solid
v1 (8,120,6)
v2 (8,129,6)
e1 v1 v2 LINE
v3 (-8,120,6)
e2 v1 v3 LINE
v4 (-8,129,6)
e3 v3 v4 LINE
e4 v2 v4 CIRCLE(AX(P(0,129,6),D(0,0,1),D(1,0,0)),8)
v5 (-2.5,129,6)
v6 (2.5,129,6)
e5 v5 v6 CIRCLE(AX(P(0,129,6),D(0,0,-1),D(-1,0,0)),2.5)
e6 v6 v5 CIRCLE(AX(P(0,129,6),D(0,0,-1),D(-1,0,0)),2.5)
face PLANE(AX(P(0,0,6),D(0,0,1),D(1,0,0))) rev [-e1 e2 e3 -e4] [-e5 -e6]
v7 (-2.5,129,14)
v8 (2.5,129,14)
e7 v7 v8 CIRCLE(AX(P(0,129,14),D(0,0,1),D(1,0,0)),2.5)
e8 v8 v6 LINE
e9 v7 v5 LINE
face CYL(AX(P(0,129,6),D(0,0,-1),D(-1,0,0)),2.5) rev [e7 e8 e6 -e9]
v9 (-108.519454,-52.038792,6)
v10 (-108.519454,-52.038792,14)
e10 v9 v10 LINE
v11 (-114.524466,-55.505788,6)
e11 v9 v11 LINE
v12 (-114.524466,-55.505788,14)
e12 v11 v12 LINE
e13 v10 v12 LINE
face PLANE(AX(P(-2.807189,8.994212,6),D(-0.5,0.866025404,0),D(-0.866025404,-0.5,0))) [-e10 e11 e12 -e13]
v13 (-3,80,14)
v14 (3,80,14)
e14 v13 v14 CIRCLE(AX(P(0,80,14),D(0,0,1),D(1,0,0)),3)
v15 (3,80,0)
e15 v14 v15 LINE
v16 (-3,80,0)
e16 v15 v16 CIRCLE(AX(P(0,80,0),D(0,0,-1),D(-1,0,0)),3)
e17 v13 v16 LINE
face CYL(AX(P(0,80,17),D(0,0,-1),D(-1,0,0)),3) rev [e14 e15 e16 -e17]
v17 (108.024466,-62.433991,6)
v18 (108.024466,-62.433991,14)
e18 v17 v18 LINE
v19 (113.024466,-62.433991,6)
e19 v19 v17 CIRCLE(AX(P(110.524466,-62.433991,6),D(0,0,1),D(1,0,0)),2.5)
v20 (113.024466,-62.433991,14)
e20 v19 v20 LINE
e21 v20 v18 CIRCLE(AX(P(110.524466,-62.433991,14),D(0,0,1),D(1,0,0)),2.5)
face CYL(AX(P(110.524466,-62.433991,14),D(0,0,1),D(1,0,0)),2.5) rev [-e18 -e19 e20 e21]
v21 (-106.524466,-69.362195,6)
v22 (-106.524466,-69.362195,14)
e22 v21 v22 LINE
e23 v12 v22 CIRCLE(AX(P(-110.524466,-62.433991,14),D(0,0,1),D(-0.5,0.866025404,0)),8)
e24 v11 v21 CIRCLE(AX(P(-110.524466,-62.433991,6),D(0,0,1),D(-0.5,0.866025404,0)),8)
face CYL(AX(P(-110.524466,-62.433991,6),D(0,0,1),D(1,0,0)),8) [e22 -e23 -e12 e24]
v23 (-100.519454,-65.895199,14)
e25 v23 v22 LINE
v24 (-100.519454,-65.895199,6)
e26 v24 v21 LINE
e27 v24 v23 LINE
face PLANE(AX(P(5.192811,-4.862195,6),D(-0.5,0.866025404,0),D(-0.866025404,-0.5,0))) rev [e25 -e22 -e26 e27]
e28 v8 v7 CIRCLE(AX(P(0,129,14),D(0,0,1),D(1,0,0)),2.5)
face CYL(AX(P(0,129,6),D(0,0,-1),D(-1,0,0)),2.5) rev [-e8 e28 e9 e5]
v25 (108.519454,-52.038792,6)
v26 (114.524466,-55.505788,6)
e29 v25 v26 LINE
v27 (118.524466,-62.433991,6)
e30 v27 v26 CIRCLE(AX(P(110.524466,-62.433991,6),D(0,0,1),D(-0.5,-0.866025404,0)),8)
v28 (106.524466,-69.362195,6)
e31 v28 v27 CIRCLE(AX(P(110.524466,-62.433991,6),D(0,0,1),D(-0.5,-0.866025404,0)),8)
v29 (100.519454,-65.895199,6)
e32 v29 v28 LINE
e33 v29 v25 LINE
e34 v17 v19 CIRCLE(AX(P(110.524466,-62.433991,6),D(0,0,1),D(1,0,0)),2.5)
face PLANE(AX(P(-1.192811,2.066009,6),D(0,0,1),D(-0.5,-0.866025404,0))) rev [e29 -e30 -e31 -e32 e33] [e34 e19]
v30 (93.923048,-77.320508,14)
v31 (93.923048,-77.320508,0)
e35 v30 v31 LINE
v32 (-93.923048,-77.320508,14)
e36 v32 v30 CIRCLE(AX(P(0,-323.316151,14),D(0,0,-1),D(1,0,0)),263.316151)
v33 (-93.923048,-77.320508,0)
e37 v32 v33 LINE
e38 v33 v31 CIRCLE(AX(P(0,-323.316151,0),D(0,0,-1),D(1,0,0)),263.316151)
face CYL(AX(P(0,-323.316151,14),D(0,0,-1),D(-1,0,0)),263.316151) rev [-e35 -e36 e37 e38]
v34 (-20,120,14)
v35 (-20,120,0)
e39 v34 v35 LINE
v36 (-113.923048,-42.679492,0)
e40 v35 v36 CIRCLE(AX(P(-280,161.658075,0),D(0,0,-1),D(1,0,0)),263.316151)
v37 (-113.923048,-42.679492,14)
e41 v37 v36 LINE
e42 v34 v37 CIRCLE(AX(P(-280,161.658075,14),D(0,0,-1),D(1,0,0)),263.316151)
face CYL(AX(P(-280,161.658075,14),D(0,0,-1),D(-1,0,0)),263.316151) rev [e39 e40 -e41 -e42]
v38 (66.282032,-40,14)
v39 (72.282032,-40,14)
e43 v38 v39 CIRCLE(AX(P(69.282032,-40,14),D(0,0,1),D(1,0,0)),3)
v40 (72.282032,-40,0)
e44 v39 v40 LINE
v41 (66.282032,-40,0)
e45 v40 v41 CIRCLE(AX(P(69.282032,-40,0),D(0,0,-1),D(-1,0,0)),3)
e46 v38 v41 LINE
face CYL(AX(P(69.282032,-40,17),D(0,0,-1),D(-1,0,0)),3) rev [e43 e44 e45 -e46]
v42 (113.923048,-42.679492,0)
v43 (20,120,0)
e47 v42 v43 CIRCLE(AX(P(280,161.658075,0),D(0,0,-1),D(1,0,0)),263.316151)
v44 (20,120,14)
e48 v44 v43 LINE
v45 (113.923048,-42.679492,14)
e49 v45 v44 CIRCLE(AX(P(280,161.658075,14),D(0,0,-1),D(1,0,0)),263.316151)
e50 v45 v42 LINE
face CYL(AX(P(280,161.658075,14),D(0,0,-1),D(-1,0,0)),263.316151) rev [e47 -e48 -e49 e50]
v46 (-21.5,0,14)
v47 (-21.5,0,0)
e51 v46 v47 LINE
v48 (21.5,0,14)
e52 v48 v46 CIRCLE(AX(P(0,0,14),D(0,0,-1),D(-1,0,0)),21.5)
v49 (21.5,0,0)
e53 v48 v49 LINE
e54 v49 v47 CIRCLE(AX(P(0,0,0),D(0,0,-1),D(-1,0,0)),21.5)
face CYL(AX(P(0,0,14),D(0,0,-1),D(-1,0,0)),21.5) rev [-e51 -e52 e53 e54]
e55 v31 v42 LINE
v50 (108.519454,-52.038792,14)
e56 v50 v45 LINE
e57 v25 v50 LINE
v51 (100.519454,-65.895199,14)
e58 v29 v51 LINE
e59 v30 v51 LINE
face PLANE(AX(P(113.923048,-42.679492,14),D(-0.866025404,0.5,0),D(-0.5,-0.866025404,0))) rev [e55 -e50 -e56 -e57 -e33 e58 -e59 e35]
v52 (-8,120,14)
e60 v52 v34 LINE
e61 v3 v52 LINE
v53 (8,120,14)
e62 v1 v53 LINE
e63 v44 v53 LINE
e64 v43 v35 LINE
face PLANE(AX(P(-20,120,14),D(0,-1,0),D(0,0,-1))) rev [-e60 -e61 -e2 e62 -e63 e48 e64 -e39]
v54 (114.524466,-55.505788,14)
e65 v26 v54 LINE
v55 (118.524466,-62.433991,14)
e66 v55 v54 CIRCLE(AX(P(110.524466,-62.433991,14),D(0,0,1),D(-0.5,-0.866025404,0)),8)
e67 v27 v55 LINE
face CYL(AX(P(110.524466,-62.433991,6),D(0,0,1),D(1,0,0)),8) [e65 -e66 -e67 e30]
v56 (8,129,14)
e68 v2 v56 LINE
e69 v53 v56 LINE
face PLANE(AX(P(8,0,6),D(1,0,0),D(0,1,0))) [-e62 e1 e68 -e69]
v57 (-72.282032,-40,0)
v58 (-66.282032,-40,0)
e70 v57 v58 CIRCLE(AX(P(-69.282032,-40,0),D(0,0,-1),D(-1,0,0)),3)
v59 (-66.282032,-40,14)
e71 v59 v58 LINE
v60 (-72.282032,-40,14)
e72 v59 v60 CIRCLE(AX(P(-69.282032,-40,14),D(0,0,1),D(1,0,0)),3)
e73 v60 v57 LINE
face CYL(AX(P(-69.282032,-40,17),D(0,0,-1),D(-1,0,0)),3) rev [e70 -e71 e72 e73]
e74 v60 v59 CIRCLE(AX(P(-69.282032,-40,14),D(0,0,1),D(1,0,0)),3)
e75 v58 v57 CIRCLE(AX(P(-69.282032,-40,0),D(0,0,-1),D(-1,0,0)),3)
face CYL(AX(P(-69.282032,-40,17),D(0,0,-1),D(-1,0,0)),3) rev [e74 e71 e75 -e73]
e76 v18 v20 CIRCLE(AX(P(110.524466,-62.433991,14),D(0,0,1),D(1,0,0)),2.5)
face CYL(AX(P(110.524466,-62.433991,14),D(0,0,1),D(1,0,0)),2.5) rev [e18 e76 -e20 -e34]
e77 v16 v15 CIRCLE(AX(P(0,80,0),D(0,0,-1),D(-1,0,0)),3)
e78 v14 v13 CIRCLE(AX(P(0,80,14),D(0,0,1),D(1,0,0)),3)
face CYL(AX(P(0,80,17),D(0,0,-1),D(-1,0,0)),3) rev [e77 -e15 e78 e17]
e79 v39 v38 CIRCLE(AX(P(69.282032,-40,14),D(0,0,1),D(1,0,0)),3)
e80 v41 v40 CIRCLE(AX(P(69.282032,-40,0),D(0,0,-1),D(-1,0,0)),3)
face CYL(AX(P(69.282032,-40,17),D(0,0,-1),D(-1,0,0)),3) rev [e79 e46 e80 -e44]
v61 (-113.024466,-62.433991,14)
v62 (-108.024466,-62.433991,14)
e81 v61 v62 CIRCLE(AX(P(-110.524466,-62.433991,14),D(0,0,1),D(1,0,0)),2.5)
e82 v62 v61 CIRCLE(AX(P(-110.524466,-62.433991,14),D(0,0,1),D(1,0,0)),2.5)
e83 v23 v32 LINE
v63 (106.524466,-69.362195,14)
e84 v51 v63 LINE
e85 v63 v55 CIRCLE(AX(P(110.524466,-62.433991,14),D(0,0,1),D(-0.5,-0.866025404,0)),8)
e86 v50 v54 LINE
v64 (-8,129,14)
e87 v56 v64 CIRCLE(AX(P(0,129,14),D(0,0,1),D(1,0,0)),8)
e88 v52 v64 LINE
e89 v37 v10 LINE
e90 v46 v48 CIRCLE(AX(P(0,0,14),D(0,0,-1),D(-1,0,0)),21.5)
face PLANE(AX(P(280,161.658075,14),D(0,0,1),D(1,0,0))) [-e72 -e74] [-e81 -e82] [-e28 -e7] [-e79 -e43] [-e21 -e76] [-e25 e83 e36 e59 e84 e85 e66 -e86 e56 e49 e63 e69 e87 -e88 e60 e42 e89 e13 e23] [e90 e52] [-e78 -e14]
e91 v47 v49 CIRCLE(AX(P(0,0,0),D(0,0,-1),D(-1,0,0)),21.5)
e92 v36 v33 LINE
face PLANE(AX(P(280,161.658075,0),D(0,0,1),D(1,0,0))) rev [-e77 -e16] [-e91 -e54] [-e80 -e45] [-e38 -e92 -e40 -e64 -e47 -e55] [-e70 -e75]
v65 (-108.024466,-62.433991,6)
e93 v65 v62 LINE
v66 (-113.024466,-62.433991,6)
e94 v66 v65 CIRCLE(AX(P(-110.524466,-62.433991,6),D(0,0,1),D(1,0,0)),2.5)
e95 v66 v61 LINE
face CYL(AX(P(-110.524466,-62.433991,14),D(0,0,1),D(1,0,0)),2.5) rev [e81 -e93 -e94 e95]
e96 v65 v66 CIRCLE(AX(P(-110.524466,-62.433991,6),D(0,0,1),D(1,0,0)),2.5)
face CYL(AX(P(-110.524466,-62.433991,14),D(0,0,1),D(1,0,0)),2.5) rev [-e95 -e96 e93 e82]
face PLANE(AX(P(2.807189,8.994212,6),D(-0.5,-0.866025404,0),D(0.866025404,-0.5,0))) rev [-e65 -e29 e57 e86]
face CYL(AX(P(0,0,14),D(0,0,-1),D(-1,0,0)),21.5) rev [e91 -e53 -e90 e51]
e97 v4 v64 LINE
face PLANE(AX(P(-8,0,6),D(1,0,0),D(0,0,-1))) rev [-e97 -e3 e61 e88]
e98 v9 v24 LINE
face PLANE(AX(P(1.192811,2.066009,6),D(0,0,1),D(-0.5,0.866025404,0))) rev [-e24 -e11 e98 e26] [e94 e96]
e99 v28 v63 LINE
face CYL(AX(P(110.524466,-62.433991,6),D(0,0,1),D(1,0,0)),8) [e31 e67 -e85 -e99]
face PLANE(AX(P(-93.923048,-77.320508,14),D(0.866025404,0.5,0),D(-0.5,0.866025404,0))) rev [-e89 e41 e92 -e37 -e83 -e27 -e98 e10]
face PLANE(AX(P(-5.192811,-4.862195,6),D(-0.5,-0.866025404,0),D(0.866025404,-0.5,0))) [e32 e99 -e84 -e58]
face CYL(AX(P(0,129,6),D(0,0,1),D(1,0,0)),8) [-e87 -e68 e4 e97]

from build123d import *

# Parameters (mm, degrees)
BOSS_EXTRUDE1_DEPTH   = 14
BOSS_EXTRUDE2_DEPTH   = 8
CIRPATTERN1_COUNT     = 3
M6_TAPPED_HOLE1_D     = 5
M6_TAPPED_HOLE1_DEPTH = 15
M6_TAPPED_HOLE1_TIP   = 1.502151548
SKETCH5_R             = 21.5
CUT_EXTRUDE1_DEPTH    = 182.6949343
M6_TAPPED_HOLE2_D     = 5
M6_TAPPED_HOLE2_DEPTH = 15
M6_TAPPED_HOLE2_TIP   = 1.502151548
SKETCH7_R             = 3
CUT_EXTRUDE2_DEPTH    = 17


with BuildPart() as part:
    # Sketch2 → Boss-Extrude1 (new body)
    with BuildSketch(Plane.XY):
        with BuildLine():
            Line((-20, 120), (20, 120))
            ThreePointArc((20, 120), (51.961524227, 30), (113.923048454, -42.679491924))
            Line((113.923048454, -42.679491924), (93.923048454, -77.320508076))
            ThreePointArc((93.923048454, -77.320508076), (0, -60), (-93.923048454, -77.320508076))
            Line((-93.923048454, -77.320508076), (-113.923048454, -42.679491924))
            ThreePointArc((-113.923048454, -42.679491924), (-51.961524227, 30), (-20, 120))
        make_face()
    extrude(amount=BOSS_EXTRUDE1_DEPTH)

    # Sketch3 → Boss-Extrude2 (add)
    with BuildSketch(Plane.XY.offset(14)):
        with BuildLine():
            ThreePointArc((-8, 129), (0, 121), (8, 129))
            Line((8, 129), (-8, 129))
        make_face()
        with BuildLine():
            Line((-8, 129), (8, 129))
            ThreePointArc((8, 129), (0, 137), (-8, 129))
        make_face()
        with BuildLine():
            ThreePointArc((-8, 129), (0, 121), (8, 129))
            Line((8, 129), (-8, 129))
        make_face()
        with BuildLine():
            Line((-8, 129), (8, 129))
            ThreePointArc((8, 129), (0, 137), (-8, 129))
        make_face()
        with BuildLine():
            Line((-8, 120), (8, 120))
            Line((8, 120), (8, 129))
            ThreePointArc((8, 129), (0, 121), (-8, 129))
            Line((-8, 129), (-8, 120))
        make_face()
    boss_extrude2 = extrude(amount=-BOSS_EXTRUDE2_DEPTH)

    # CirPattern1: Boss-Extrude2 ×3 about axis
    cirpattern1_axis = Axis((0, 1.377339071, 0), (0, 0, 1))
    for i in range(1, CIRPATTERN1_COUNT):
        add(boss_extrude2.rotate(cirpattern1_axis, i * 360 / CIRPATTERN1_COUNT))

    # M6 Tapped Hole1
    with Locations(Plane(origin=(0, 129, 6), x_dir=(-1, 0, 0), z_dir=(0, 0, -1))):
        with Locations((0, 0)):
            Hole(M6_TAPPED_HOLE1_D / 2, depth=M6_TAPPED_HOLE1_DEPTH)
            with Locations((0, 0, -(M6_TAPPED_HOLE1_DEPTH + M6_TAPPED_HOLE1_TIP / 2))):  # 118° drill point
                Cone(0, M6_TAPPED_HOLE1_D / 2, M6_TAPPED_HOLE1_TIP, mode=Mode.SUBTRACT)

    # Sketch5 → Cut-Extrude1 (cut, through all)
    with BuildSketch(Plane(origin=(0, 0, 0), x_dir=(-1, 0, 0), z_dir=(0, 0, -1))):
        Circle(SKETCH5_R)
    extrude(amount=-CUT_EXTRUDE1_DEPTH, mode=Mode.SUBTRACT)

    # M6 Tapped Hole2
    with Locations(Plane(origin=(-110.524466463, -62.433991393, 14), x_dir=(1, 0, 0), z_dir=(0, 0, 1))):
        with Locations((0, 0), (221.048932926, 0)):
            Hole(M6_TAPPED_HOLE2_D / 2, depth=M6_TAPPED_HOLE2_DEPTH)
            with Locations((0, 0, -(M6_TAPPED_HOLE2_DEPTH + M6_TAPPED_HOLE2_TIP / 2))):  # 118° drill point
                Cone(0, M6_TAPPED_HOLE2_D / 2, M6_TAPPED_HOLE2_TIP, mode=Mode.SUBTRACT)

    # Sketch7 → Cut-Extrude2 (cut)
    with BuildSketch(Plane(origin=(0, 0, 0), x_dir=(-1, 0, 0), z_dir=(0, 0, -1))):
        with Locations((0, 80)):
            Circle(SKETCH7_R)
        with Locations((69.282032303, -40)):
            Circle(SKETCH7_R)
        with Locations((-69.282032303, -40)):
            Circle(SKETCH7_R)
    extrude(amount=-CUT_EXTRUDE2_DEPTH, mode=Mode.SUBTRACT)


solid = part.part
